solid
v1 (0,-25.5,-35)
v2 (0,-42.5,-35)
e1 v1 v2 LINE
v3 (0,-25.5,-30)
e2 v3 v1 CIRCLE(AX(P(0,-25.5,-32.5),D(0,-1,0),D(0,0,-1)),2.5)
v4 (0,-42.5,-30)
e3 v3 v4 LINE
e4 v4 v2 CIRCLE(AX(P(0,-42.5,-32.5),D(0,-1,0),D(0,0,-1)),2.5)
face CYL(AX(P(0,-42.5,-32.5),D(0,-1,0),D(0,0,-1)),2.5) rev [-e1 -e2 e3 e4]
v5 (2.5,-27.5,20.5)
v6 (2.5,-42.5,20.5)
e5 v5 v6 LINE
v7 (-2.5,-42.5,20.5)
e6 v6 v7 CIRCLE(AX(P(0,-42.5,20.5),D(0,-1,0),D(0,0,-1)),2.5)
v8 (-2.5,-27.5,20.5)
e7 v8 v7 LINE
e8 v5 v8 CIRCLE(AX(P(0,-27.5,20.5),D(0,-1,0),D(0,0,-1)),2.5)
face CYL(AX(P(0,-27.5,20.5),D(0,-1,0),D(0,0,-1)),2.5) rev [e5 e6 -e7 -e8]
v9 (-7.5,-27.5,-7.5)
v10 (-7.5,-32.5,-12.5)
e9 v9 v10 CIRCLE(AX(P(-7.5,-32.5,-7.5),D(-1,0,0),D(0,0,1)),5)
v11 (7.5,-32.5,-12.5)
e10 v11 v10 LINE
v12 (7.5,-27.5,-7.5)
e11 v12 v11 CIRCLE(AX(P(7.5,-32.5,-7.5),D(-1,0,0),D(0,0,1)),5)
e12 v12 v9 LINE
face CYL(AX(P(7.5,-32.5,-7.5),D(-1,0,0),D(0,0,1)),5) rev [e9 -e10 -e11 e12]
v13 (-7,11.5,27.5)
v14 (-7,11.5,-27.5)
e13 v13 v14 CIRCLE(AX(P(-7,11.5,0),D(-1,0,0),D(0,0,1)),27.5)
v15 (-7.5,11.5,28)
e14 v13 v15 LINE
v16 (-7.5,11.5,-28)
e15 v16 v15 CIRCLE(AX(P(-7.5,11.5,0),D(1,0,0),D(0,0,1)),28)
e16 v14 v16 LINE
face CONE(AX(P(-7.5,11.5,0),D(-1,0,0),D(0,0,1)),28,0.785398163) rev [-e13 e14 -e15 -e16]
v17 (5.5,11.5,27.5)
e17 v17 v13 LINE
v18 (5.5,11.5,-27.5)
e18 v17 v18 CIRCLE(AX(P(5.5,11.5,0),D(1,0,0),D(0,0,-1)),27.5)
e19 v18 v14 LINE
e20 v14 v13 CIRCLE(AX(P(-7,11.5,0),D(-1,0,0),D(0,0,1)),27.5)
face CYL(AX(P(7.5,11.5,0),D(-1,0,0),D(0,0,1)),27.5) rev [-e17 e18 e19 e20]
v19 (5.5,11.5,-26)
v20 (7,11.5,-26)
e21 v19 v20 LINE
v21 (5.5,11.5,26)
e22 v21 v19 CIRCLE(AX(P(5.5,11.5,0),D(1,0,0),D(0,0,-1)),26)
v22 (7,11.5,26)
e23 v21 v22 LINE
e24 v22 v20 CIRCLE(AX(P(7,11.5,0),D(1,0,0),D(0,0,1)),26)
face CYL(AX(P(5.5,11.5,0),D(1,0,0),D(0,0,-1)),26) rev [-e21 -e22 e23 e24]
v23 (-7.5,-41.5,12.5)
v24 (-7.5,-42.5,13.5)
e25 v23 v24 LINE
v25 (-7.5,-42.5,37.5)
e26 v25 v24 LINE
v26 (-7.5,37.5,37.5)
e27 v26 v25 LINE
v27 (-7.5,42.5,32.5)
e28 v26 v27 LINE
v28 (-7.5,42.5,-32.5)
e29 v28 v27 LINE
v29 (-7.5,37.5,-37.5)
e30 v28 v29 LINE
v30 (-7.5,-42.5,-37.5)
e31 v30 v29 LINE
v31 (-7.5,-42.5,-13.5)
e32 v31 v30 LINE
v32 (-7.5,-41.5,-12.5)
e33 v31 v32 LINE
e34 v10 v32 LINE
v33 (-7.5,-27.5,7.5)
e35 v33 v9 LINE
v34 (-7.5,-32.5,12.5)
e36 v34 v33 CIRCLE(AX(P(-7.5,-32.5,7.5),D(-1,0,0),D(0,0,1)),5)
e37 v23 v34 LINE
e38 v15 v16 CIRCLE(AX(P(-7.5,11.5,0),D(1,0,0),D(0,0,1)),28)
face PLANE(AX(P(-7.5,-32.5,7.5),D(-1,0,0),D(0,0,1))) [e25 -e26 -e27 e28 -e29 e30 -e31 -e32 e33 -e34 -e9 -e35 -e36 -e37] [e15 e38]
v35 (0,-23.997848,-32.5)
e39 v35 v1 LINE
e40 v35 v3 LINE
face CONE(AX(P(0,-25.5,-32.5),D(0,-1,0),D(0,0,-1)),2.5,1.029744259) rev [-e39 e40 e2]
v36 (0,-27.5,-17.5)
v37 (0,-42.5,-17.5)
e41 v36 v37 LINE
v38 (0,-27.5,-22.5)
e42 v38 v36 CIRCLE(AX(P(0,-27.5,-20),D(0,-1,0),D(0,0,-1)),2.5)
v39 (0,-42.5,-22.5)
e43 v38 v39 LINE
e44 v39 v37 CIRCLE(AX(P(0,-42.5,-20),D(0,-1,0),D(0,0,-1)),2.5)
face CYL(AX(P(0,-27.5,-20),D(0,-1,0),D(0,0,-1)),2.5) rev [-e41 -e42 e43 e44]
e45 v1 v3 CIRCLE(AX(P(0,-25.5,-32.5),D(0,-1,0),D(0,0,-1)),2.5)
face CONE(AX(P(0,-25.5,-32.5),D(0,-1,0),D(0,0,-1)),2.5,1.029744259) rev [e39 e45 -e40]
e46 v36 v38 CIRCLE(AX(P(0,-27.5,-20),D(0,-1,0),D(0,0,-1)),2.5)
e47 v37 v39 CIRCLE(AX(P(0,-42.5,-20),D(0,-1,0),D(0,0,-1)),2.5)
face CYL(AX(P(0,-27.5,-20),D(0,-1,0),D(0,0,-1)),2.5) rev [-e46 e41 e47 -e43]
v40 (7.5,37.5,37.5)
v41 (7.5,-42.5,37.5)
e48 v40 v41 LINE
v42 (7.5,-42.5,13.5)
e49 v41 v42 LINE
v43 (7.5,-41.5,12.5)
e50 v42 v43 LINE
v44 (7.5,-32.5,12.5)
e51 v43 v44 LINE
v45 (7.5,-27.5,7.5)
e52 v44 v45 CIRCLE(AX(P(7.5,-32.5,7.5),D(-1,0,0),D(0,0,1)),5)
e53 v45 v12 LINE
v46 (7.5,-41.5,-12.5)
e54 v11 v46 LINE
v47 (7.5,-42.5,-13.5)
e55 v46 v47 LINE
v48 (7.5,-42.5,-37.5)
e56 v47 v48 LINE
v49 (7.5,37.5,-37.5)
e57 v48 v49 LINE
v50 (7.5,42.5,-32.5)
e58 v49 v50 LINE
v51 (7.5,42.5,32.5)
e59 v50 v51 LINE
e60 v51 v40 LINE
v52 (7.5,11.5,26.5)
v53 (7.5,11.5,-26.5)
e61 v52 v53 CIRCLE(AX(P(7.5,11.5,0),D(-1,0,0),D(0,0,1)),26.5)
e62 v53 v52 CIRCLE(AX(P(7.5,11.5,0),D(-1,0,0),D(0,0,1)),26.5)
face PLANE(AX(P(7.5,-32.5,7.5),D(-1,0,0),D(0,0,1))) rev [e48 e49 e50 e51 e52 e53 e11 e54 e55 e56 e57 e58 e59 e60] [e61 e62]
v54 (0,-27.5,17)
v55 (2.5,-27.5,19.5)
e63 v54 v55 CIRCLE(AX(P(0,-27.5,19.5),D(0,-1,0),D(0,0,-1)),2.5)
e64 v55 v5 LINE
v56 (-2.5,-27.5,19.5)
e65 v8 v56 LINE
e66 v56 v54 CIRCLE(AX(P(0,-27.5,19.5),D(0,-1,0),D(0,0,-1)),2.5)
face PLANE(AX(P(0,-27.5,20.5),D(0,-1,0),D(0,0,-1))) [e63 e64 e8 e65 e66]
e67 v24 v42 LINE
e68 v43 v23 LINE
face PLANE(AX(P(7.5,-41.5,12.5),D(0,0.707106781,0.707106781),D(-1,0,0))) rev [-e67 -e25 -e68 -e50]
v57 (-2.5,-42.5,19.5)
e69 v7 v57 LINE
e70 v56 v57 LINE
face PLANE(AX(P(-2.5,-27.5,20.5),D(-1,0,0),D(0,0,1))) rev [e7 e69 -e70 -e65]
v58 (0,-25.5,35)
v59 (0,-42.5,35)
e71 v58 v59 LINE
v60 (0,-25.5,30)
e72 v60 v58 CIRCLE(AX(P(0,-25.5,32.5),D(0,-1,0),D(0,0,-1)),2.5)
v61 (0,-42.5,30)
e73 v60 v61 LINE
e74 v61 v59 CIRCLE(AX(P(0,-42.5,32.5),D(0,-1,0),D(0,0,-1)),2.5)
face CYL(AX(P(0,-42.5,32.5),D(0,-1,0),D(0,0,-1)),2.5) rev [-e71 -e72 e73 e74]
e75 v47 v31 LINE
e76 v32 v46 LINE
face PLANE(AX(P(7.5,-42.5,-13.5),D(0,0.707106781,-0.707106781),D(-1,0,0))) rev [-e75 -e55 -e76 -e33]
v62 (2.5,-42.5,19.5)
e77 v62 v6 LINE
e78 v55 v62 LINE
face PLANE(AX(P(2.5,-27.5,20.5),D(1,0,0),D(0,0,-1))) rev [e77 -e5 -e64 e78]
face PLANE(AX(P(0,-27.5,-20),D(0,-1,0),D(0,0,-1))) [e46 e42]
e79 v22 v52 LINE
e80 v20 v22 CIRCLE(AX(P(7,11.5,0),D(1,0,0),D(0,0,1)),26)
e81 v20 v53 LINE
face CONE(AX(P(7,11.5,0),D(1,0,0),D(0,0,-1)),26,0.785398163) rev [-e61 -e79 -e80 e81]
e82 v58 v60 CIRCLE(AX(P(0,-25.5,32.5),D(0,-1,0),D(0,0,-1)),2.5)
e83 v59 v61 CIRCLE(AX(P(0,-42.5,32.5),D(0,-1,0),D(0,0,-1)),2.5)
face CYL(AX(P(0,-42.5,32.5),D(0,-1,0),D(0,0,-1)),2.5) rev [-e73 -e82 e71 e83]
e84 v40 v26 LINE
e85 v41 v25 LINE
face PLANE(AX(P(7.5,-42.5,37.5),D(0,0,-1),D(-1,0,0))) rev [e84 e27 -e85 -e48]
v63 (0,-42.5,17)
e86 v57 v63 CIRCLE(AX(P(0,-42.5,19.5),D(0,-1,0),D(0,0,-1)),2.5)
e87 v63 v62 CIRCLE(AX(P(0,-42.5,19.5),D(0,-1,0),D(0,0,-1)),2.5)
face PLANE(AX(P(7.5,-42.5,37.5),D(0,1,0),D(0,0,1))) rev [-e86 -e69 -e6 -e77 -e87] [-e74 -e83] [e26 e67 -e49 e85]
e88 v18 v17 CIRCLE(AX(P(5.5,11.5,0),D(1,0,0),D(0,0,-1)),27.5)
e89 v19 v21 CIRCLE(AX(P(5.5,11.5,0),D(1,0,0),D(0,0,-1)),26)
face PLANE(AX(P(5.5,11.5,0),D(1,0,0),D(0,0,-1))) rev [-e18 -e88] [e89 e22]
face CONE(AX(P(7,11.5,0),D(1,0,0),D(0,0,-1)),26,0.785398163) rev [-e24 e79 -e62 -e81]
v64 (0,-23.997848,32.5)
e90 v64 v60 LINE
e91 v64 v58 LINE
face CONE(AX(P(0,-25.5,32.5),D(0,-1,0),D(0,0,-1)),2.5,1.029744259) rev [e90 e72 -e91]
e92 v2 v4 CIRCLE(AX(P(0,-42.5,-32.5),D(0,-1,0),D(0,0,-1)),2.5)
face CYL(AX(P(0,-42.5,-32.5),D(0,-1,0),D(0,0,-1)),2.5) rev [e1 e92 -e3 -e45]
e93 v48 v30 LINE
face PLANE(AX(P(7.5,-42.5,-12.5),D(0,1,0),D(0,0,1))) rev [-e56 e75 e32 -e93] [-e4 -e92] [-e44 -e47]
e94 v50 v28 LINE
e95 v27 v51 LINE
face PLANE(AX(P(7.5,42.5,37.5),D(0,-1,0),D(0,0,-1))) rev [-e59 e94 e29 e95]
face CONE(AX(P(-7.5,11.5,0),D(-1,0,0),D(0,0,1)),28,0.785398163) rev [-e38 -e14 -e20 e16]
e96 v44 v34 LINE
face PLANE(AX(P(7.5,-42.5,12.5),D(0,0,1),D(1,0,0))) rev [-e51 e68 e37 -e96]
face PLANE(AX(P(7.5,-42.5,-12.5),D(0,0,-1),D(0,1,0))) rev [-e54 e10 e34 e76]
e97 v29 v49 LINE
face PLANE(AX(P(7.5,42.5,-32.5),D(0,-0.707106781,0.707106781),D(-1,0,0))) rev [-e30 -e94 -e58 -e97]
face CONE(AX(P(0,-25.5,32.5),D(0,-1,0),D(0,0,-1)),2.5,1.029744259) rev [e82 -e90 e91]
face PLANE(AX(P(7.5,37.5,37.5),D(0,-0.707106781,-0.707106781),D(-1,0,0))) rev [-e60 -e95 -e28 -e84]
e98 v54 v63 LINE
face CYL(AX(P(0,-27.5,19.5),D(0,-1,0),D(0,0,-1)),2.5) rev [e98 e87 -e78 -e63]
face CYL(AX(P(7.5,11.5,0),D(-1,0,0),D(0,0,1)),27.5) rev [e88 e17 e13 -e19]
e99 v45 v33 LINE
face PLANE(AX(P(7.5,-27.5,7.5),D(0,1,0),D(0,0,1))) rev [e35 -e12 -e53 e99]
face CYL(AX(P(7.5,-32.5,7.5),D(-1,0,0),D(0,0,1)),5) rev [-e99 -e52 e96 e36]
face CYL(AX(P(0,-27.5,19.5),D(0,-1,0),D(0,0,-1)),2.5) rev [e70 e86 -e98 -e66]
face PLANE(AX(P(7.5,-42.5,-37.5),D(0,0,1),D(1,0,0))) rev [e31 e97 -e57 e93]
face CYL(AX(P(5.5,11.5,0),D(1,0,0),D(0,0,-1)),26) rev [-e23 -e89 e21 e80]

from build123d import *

# Parameters (mm, degrees)
SKETCH1_R             = 27.5
BOSS_EXTRUDE2_DEPTH   = 7.5
M6_TAPPED_HOLE1_D     = 5
M6_TAPPED_HOLE1_DEPTH = 17
M6_TAPPED_HOLE1_TIP   = 1.502151548
BOSS_EXTRUDE3_START   = -2
SKETCH5_R             = 27.5
SKETCH5_R_2           = 26
BOSS_EXTRUDE3_DEPTH   = 2
CHAMFER1_SIZE         = 5
SKETCH4_R             = 2.5
CUT_EXTRUDE1_DEPTH    = 15
CHAMFER2_SIZE         = 1
CHAMFER3_SIZE         = 0.5


with BuildPart() as part:
    # Sketch1 → Boss-Extrude2 (new, symmetric)
    with BuildSketch(Plane(origin=(0, 0, 0), x_dir=(0, 0, -1), z_dir=(1, 0, 0))):
        with BuildLine():
            Line((-37.5, -42.5), (-12.5, -42.5))
            Line((-12.5, -42.5), (-12.5, -32.5))
            ThreePointArc((-12.5, -32.5), (-11.035533906, -28.964466094), (-7.5, -27.5))
            Line((-7.5, -27.5), (7.5, -27.5))
            ThreePointArc((7.5, -27.5), (11.035533906, -28.964466094), (12.5, -32.5))
            Line((12.5, -32.5), (12.5, -42.5))
            Line((12.5, -42.5), (37.5, -42.5))
            Line((37.5, -42.5), (37.5, 42.5))
            Line((37.5, 42.5), (-37.5, 42.5))
            Line((-37.5, 42.5), (-37.5, -42.5))
        make_face()
        with Locations((0, 11.5)):
            Circle(SKETCH1_R, mode=Mode.SUBTRACT)
    extrude(amount=BOSS_EXTRUDE2_DEPTH, both=True)

    # M6 Tapped Hole1
    with Locations(Plane(origin=(0, -42.5, 0), x_dir=(-1, 0, 0), z_dir=(0, -1, 0))):
        with Locations((0, -32.5), (0, 32.5)):
            Hole(M6_TAPPED_HOLE1_D / 2, depth=M6_TAPPED_HOLE1_DEPTH)
            with Locations((0, 0, -(M6_TAPPED_HOLE1_DEPTH + M6_TAPPED_HOLE1_TIP / 2))):  # 118° drill point
                Cone(0, M6_TAPPED_HOLE1_D / 2, M6_TAPPED_HOLE1_TIP, mode=Mode.SUBTRACT)

    # Sketch5 → Boss-Extrude3 (add)
    with BuildSketch(Plane(origin=(7.5, 0, 0), x_dir=(0, 0, -1), z_dir=(1, 0, 0)).offset(BOSS_EXTRUDE3_START)):
        with Locations((0, 11.5)):
            Circle(SKETCH5_R)
        with Locations((0, 11.5)):
            Circle(SKETCH5_R_2, mode=Mode.SUBTRACT)
    extrude(amount=BOSS_EXTRUDE3_DEPTH)

    # Chamfer1
    chamfer1_edges = [part.edges().sort_by_distance(p)[0] for p in [
        (0, 42.5, 37.5),
        (0, 42.5, -37.5),
    ]]
    chamfer(chamfer1_edges, length=CHAMFER1_SIZE)

    # Sketch4 → Cut-Extrude1 (cut)
    with BuildSketch(Plane.XZ.offset(42.5)):
        with Locations(Location((0, -20, 0), (0, 0, 270))):
            Circle(SKETCH4_R)
        with BuildLine():
            Line((2.5, 20.5), (2.5, 19.5))
            ThreePointArc((2.5, 19.5), (0, 17), (-2.5, 19.5))
            Line((-2.5, 19.5), (-2.5, 20.5))
            ThreePointArc((-2.5, 20.5), (0, 23), (2.5, 20.5))
        make_face()
    extrude(amount=-CUT_EXTRUDE1_DEPTH, mode=Mode.SUBTRACT)

    # Chamfer2
    chamfer2_edges = [part.edges().sort_by_distance(p)[0] for p in [
        (0, -42.5, -12.5),
        (0, -42.5, 12.5),
    ]]
    chamfer(chamfer2_edges, length=CHAMFER2_SIZE)

    # Chamfer3
    chamfer3_edges = [part.edges().sort_by_distance(p)[0] for p in [
        (-7.5, 11.5, 27.5),
        (7.5, 11.5, 26),
    ]]
    chamfer(chamfer3_edges, length=CHAMFER3_SIZE)


solid = part.part
